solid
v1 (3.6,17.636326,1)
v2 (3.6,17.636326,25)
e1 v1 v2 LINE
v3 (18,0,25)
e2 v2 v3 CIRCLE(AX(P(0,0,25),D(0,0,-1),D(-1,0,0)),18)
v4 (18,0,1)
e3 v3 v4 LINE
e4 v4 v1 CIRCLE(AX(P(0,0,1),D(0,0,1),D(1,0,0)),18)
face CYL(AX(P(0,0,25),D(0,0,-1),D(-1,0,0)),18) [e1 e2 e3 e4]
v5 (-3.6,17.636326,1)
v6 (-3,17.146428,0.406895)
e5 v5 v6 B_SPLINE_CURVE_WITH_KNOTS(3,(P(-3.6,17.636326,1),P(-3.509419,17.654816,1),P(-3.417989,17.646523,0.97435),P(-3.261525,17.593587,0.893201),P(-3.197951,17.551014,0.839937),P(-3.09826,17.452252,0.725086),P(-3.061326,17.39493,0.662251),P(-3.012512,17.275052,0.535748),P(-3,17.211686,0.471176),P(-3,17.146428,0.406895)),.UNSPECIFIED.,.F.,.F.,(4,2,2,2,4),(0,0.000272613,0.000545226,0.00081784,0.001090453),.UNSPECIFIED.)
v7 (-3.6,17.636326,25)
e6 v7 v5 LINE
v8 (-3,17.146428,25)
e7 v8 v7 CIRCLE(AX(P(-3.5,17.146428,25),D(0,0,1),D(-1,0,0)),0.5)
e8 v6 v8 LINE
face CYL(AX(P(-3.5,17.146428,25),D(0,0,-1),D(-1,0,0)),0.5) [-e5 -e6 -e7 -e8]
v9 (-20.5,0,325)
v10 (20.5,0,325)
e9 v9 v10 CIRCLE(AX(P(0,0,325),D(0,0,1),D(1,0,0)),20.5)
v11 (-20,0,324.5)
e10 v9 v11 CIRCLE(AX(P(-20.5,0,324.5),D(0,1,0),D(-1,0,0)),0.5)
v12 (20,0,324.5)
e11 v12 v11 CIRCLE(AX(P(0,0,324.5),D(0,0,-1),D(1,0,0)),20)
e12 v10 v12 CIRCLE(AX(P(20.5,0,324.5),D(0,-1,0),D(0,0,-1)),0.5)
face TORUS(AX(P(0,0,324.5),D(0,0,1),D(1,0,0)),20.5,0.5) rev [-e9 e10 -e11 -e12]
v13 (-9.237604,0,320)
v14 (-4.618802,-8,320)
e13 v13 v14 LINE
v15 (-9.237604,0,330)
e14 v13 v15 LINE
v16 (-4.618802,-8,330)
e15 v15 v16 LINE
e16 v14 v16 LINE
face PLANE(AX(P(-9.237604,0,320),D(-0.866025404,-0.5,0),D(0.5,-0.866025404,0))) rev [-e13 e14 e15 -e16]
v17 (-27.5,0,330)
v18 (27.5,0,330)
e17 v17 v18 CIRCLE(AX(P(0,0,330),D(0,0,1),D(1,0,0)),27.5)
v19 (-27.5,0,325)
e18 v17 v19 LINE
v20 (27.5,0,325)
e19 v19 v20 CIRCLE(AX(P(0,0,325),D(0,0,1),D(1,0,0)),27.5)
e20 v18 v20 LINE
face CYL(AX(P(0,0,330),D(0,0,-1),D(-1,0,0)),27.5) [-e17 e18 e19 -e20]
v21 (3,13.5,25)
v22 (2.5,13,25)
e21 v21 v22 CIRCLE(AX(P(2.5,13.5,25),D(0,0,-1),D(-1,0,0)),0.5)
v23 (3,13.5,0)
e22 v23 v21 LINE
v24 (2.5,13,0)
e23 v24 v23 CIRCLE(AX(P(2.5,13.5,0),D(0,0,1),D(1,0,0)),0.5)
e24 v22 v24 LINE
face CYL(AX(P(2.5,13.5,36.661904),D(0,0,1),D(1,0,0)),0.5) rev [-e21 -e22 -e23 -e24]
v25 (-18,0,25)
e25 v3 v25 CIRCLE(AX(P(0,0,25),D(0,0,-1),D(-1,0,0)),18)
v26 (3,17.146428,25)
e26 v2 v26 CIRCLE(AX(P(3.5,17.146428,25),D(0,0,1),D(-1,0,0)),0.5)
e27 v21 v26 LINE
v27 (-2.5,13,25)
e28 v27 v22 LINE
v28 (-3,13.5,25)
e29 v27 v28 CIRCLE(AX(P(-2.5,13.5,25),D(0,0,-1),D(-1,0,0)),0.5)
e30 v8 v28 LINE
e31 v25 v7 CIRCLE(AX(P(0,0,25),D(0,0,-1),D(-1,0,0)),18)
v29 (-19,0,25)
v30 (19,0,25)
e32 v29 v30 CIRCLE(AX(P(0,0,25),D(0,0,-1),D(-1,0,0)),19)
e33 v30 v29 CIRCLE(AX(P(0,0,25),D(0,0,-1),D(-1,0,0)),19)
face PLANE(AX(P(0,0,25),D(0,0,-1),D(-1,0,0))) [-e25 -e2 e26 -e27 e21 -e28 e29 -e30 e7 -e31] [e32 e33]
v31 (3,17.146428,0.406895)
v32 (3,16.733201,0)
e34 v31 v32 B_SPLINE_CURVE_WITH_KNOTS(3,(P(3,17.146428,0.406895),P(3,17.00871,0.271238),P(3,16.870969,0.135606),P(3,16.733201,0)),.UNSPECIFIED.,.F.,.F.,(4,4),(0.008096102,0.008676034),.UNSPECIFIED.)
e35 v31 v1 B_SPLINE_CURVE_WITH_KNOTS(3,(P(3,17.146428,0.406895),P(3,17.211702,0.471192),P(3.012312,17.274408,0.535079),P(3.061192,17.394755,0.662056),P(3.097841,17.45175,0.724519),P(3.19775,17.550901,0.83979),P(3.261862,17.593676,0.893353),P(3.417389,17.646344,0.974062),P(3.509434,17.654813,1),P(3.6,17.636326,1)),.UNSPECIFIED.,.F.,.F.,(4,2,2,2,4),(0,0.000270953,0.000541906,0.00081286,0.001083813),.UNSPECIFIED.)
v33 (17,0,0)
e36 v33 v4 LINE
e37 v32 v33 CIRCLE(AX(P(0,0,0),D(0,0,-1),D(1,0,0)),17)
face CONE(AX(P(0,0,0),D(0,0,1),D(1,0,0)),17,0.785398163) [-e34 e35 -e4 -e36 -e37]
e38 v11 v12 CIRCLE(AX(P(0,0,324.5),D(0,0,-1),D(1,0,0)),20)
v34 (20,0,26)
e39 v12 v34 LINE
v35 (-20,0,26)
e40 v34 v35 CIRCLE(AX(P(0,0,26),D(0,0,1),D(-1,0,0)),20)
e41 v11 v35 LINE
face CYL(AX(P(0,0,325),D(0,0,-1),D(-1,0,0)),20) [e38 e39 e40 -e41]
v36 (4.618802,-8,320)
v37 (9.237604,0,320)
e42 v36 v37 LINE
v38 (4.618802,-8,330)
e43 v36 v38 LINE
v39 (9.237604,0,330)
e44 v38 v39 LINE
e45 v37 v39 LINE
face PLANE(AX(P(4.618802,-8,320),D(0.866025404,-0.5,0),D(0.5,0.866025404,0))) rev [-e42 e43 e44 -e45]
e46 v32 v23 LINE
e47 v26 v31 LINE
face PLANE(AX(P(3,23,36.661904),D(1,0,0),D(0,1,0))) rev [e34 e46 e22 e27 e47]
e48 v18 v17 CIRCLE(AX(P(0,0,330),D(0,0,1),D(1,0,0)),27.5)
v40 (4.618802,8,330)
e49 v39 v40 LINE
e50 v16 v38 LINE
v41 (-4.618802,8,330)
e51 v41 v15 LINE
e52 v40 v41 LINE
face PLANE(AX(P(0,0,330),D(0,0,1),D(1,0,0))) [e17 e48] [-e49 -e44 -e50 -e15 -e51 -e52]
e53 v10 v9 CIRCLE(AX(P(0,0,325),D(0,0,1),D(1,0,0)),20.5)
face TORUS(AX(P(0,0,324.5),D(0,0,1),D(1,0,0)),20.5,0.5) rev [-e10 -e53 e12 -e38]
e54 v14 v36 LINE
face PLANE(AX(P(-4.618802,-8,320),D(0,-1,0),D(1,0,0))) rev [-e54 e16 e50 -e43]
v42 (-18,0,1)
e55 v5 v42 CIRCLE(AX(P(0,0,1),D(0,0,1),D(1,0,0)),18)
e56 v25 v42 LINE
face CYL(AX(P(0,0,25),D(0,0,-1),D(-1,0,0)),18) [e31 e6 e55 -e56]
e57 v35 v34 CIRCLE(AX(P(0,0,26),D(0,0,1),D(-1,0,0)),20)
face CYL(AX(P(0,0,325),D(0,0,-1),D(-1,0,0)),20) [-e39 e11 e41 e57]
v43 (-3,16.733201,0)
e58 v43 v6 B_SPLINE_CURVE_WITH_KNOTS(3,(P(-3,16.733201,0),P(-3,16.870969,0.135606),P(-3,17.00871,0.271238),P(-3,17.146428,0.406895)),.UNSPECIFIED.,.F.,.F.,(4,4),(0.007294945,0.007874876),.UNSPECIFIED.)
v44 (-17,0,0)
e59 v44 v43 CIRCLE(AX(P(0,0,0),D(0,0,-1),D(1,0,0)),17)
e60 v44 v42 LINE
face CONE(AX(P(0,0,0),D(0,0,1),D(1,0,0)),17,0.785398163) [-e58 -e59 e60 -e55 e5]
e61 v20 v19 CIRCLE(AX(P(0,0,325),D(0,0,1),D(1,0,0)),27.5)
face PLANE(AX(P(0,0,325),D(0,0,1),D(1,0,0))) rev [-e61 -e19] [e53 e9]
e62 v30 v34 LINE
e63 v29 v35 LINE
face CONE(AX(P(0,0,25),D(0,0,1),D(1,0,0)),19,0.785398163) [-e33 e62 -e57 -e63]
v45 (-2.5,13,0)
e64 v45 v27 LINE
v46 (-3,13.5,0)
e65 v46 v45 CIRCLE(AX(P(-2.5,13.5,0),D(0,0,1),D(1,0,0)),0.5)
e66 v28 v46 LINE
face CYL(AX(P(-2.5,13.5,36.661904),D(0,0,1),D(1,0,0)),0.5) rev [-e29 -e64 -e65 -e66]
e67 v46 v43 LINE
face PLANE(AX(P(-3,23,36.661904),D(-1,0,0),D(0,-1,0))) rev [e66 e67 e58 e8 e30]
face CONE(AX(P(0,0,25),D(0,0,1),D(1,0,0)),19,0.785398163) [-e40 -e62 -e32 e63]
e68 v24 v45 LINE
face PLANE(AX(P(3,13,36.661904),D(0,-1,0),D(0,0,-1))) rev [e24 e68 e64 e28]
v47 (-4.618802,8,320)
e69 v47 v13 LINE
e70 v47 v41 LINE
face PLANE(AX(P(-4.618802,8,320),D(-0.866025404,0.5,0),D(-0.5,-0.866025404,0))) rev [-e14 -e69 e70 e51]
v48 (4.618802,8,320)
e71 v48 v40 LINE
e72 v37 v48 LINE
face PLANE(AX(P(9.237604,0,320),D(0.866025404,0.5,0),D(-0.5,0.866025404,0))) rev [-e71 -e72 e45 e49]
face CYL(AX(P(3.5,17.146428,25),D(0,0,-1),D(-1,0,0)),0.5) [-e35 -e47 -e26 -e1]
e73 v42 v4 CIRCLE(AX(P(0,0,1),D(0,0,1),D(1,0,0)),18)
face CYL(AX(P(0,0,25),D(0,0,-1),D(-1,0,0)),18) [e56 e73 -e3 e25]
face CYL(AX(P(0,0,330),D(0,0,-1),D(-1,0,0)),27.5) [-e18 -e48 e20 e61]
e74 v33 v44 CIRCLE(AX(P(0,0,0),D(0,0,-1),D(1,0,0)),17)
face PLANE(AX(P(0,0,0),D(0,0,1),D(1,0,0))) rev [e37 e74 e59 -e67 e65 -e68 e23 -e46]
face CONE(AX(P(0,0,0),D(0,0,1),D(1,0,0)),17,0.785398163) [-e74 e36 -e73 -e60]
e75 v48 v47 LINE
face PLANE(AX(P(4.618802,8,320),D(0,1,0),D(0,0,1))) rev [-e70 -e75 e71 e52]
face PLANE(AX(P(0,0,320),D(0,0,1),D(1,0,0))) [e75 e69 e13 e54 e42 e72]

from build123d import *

# Parameters (mm, degrees)
SKETCH_1_R          = 20
EXTRUDE_1_DEPTH     = 325
SKETCH_2_R          = 27.5
EXTRUDE_2_DEPTH     = 5
CUT_EXTRUDE_1_DEPTH = 10
SKETCH_4_OUTSIDE_W  = 124.808
SKETCH_4_OUTSIDE_H  = 124.808
SKETCH_4_OUTSIDE_R  = 18
CUT_EXTRUDE_2_DEPTH = 25
CHAMFER_1_SIZE      = 1
CHAMFER_2_SIZE      = 1
FILLET_1_R          = 0.5
SKETCH_5_W          = 6
SKETCH_5_H          = 10
CUT_EXTRUDE_3_DEPTH = 25
FILLET_2_R          = 0.5


with BuildPart() as part:
    # 草图1 → 凸台-拉伸1 (new body)
    with BuildSketch(Plane.XY):
        Circle(SKETCH_1_R)
    extrude(amount=EXTRUDE_1_DEPTH)

    # 草图2 → 凸台-拉伸2 (add)
    with BuildSketch(Plane.XY.offset(325)):
        Circle(SKETCH_2_R)
    extrude(amount=EXTRUDE_2_DEPTH)

    # 草图3 → 切除-拉伸1 (cut)
    with BuildSketch(Plane.XY.offset(330)):
        Polygon((9.237604307, 0), (4.618802154, 8), (-4.618802154, 8), (-9.237604307, 0), (-4.618802154, -8), (4.618802154, -8), align=None)
    extrude(amount=-CUT_EXTRUDE_1_DEPTH, mode=Mode.SUBTRACT)

    # 草图4 outside → 切除-拉伸2 (cut)
    with BuildSketch(Plane(origin=(0, 0, 0), x_dir=(-1, 0, 0), z_dir=(0, 0, -1))):
        Rectangle(SKETCH_4_OUTSIDE_W, SKETCH_4_OUTSIDE_H)
        Circle(SKETCH_4_OUTSIDE_R, mode=Mode.SUBTRACT)
    extrude(amount=-CUT_EXTRUDE_2_DEPTH, mode=Mode.SUBTRACT)

    # 倒角1
    chamfer_1_edges = [part.edges().sort_by_distance(p)[0] for p in [
        (-20, 0, 25),
    ]]
    chamfer(chamfer_1_edges, length=CHAMFER_1_SIZE)

    # 倒角2
    chamfer_2_edges = [part.edges().sort_by_distance(p)[0] for p in [
        (18, 0, 0),
    ]]
    chamfer(chamfer_2_edges, length=CHAMFER_2_SIZE)

    # 圆角1
    fillet_1_edges = [part.edges().sort_by_distance(p)[0] for p in [
        (-20, 0, 325),
    ]]
    fillet(fillet_1_edges, radius=FILLET_1_R)

    # 草图5 → 切除-拉伸3 (cut)
    with BuildSketch(Plane(origin=(0, 0, 0), x_dir=(-1, 0, 0), z_dir=(0, 0, -1))):
        with Locations((0, 18)):
            Rectangle(SKETCH_5_W, SKETCH_5_H)
    extrude(amount=-CUT_EXTRUDE_3_DEPTH, mode=Mode.SUBTRACT)

    # 圆角2
    fillet_2_edges = [part.edges().sort_by_distance(p)[0] for p in [
        (-3, 13, 12.5),
        (3, 13, 12.5),
        (3, 17.748239349, 13),
        (-3, 17.748239349, 13),
    ]]
    fillet(fillet_2_edges, radius=FILLET_2_R)


solid = part.part
